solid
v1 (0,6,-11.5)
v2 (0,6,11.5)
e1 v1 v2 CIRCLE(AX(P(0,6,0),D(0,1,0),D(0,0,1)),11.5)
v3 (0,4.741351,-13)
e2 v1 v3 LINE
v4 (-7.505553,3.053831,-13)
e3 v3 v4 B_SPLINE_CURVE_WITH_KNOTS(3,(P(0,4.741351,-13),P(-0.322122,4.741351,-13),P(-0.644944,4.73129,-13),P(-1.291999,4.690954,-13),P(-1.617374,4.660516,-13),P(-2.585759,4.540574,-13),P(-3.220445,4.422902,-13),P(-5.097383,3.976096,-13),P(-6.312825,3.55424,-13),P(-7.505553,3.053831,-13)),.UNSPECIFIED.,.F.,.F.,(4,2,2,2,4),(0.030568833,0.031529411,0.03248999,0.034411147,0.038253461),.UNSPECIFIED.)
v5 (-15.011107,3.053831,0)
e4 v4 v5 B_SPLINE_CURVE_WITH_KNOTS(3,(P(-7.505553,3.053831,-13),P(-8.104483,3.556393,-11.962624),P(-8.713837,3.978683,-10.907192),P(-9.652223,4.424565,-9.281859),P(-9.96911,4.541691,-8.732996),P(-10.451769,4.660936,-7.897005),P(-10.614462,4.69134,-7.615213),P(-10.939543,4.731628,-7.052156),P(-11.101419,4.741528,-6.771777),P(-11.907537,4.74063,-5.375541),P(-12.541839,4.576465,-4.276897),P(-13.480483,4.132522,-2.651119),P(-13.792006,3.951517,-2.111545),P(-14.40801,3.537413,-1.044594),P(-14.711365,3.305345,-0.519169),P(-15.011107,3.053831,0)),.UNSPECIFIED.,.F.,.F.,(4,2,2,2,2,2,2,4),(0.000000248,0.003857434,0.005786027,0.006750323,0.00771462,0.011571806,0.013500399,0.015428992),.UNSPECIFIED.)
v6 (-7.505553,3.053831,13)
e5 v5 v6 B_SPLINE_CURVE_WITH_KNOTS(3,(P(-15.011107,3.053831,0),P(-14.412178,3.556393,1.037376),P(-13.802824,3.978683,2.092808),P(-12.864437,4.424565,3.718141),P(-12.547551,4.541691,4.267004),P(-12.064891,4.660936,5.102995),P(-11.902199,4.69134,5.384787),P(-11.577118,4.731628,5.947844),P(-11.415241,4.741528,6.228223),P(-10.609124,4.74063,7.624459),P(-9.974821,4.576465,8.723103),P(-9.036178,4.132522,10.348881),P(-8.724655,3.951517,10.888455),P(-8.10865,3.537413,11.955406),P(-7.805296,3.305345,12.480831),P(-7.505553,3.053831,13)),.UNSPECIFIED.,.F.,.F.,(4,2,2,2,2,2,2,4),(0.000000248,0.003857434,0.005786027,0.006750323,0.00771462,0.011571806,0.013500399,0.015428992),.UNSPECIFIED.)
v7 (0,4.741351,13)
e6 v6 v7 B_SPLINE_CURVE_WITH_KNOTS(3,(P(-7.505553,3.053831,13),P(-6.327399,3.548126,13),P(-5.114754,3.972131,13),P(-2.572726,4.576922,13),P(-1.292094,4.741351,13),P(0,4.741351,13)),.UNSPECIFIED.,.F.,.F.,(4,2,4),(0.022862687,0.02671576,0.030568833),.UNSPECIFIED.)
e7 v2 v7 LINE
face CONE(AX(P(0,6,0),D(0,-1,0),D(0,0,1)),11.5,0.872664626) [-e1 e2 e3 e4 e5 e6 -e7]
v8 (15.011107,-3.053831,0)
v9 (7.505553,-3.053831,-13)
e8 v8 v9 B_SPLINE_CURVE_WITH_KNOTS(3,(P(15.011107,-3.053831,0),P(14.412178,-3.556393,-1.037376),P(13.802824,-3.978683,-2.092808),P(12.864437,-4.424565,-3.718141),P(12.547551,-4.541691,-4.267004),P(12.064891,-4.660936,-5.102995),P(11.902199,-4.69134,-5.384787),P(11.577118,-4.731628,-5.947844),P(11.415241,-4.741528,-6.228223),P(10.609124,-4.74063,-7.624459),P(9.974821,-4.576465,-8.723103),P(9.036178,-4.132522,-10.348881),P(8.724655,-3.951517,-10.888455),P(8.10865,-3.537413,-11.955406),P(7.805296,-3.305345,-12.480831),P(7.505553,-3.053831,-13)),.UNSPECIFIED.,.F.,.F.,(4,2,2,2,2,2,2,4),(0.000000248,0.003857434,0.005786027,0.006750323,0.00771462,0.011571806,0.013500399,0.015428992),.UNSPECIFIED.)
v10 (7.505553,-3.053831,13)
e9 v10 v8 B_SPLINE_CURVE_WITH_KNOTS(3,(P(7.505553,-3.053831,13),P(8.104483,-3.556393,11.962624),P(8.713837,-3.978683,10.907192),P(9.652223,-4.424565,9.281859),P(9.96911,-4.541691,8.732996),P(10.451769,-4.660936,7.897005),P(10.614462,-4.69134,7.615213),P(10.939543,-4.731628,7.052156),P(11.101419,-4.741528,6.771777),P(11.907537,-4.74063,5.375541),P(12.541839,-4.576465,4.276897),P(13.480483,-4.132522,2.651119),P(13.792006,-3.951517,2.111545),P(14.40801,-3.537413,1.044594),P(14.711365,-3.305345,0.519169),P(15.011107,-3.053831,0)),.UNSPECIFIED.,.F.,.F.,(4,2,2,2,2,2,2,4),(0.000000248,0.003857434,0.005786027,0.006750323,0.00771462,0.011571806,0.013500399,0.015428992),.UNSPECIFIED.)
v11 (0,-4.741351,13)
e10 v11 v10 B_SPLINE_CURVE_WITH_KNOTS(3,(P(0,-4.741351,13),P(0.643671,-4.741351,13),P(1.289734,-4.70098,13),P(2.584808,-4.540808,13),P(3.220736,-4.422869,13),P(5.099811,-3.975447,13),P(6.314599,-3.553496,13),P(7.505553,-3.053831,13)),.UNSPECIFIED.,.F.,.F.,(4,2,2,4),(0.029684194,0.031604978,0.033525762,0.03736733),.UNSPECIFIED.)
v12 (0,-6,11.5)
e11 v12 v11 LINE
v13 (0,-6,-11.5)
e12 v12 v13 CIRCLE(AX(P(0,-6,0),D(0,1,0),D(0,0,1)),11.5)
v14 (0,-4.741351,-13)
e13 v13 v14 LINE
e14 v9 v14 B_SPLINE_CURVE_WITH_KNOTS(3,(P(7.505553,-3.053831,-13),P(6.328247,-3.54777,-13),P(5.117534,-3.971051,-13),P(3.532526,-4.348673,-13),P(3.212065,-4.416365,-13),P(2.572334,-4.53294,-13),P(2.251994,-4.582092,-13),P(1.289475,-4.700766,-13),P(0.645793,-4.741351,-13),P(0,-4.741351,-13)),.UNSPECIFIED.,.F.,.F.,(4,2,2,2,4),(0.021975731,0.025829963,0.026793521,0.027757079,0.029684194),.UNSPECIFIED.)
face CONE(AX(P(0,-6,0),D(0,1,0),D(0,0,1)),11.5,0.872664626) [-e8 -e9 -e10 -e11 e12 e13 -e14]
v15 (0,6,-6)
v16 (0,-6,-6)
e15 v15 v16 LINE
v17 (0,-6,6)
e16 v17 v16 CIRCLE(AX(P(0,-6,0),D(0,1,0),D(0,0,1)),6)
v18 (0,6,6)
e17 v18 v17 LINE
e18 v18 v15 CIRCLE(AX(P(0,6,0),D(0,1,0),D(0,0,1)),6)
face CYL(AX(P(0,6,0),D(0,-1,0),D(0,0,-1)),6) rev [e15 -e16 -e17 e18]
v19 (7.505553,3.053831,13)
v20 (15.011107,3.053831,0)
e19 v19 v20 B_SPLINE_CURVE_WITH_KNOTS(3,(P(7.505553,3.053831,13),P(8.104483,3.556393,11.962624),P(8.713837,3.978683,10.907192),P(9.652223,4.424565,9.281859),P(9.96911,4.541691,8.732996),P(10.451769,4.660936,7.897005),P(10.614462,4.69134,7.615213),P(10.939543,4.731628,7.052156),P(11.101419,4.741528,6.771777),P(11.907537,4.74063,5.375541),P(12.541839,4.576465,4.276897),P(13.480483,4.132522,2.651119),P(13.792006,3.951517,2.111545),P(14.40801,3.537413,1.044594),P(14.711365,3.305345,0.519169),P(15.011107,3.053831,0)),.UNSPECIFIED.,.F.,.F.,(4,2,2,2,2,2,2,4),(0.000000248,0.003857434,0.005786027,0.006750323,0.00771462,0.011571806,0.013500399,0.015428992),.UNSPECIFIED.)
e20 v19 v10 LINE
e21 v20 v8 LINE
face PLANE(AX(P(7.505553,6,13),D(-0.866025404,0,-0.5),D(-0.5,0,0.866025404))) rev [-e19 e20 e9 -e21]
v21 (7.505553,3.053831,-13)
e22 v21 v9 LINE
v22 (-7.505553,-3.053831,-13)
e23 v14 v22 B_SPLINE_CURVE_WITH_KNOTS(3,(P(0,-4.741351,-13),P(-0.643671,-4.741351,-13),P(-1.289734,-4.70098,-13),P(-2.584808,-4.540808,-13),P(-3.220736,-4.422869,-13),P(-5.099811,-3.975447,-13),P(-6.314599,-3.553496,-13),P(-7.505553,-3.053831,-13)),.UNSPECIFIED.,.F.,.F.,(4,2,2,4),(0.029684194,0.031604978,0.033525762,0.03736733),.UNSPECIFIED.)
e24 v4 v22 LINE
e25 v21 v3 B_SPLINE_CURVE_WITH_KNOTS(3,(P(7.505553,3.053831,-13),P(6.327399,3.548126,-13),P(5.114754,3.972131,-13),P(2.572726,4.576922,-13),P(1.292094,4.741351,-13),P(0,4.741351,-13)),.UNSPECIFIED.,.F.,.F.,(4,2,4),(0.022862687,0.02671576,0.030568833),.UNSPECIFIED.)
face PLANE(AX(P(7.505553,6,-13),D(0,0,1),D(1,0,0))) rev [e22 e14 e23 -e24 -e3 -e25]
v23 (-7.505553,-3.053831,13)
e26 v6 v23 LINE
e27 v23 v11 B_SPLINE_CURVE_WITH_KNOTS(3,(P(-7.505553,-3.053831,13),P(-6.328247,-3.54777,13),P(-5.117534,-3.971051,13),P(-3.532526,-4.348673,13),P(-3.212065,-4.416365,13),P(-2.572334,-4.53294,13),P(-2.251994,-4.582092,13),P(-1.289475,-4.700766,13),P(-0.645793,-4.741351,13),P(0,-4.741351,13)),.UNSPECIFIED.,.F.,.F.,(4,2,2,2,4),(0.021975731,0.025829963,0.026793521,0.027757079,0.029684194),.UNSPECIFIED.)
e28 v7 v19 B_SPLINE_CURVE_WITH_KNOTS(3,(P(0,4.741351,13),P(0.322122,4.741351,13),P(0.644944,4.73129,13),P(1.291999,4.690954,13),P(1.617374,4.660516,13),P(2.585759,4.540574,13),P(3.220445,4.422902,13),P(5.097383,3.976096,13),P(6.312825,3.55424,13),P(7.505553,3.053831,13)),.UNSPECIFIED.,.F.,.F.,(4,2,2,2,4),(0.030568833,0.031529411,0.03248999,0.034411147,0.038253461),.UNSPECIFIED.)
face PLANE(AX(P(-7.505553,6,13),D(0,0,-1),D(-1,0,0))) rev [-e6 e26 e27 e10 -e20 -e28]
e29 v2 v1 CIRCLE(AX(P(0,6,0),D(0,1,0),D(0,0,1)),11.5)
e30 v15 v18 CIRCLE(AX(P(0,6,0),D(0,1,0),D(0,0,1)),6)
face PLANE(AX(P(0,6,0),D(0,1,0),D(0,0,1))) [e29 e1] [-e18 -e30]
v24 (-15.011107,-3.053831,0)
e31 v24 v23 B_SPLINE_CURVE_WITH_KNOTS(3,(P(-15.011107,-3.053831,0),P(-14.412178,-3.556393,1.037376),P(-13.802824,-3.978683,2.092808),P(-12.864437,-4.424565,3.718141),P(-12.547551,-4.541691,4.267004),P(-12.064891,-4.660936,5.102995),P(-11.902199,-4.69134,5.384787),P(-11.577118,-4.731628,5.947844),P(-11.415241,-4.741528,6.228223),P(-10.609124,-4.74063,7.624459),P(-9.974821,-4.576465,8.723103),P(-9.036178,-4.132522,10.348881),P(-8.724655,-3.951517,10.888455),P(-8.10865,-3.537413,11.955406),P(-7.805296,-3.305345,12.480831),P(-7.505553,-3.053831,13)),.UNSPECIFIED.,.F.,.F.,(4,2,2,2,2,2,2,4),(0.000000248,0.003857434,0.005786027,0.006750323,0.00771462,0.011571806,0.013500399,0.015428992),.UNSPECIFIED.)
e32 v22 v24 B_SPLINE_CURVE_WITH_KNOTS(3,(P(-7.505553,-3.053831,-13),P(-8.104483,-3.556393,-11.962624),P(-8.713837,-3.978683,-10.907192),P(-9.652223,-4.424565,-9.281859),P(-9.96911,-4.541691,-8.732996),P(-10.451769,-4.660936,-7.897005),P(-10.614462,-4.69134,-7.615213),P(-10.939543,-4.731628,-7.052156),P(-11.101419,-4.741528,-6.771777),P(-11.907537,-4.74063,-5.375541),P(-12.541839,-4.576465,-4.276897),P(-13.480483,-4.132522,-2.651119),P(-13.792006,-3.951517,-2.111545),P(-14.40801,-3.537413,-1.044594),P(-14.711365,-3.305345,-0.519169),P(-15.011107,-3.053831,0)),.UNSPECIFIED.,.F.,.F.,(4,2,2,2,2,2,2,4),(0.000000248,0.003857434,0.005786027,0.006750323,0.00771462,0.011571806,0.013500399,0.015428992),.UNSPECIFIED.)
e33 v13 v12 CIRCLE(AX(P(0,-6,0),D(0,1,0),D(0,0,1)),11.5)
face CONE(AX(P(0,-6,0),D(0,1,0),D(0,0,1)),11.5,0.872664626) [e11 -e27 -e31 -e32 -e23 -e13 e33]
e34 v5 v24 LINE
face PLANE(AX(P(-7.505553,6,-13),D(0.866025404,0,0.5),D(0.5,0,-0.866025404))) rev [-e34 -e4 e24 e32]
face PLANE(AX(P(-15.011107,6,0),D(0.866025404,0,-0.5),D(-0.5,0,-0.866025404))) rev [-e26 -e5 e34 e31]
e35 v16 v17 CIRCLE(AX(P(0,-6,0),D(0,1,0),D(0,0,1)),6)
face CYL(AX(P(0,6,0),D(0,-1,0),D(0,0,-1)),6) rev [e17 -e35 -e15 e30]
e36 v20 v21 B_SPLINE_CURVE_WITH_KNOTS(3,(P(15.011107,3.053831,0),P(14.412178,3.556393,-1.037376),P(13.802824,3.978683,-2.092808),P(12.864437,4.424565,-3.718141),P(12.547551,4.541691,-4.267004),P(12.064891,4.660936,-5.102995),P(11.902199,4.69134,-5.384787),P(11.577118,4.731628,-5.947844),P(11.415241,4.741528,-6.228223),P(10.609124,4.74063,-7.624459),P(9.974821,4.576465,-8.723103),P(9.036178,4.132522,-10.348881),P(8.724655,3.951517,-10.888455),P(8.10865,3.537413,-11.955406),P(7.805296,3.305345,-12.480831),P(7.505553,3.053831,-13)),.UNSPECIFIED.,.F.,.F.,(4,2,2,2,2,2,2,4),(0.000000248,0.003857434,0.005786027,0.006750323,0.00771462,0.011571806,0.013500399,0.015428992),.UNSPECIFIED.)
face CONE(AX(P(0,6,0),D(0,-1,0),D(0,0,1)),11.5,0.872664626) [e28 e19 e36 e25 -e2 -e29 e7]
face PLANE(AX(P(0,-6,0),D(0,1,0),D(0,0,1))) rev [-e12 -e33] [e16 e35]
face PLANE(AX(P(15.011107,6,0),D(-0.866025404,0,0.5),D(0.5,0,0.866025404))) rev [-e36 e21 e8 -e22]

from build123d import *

# Parameters (mm, degrees)
HEX_NUT_PROFILE_R                     = 6
HEX_NUT_BODY_DEPTH                    = 6
CHAMFER_CIRCLE_23_OUTSIDE_W           = 98.006
CHAMFER_CIRCLE_23_OUTSIDE_H           = 93.984
CHAMFER_CIRCLE_23_OUTSIDE_R           = 11.5
CORNER_CHAMFER_50_DEPTH               = 24.202011407
CORNER_CHAMFER_50_DRAFT               = -50
CORNER_CHAMFER_MIRROR_COPY_1_SKETCH_W = 98.006
CORNER_CHAMFER_MIRROR_COPY_1_SKETCH_H = 93.984
CORNER_CHAMFER_MIRROR_COPY_1_SKETCH_R = 11.5
CORNER_CHAMFER_MIRROR_COPY_1_DEPTH    = 24.202011407
CORNER_CHAMFER_MIRROR_COPY_1_DRAFT    = -50


with BuildPart() as part:
    # Hex Nut Profile → Hex Nut Body (new, symmetric)
    with BuildSketch(Plane(origin=(0, 0, 0), x_dir=(1, 0, 0), z_dir=(0, 1, 0))):
        Polygon((15.011106999, 0), (7.505553499, 13), (-7.505553499, 13), (-15.011106999, 0), (-7.505553499, -13), (7.505553499, -13), align=None)
        with Locations(Location((0, 0, 0), (0, 0, 270))):
            Circle(HEX_NUT_PROFILE_R, mode=Mode.SUBTRACT)
    extrude(amount=HEX_NUT_BODY_DEPTH, both=True)


with BuildPart() as corner_chamfer_50_tool:
    # Chamfer Circle Ø23 outside → Corner Chamfer 50° (with draft: the straight prism first)
    with BuildSketch(Plane(origin=(0, 6, 0), x_dir=(1, 0, 0), z_dir=(0, 1, 0))):
        Rectangle(CHAMFER_CIRCLE_23_OUTSIDE_W, CHAMFER_CIRCLE_23_OUTSIDE_H)
        Circle(CHAMFER_CIRCLE_23_OUTSIDE_R, mode=Mode.SUBTRACT)
    extrude(amount=-CORNER_CHAMFER_50_DEPTH)
    # Corner Chamfer 50°: the draft: its side faces are tilted about the plane it starts from
    corner_chamfer_50_sides = [corner_chamfer_50_tool.faces().sort_by_distance(p)[0] for p in [
        (0, -6.101005704, 46.992),
        (49.003, -6.101005704, 0),
        (0, -6.101005704, -46.992),
        (-49.003, -6.101005704, 0),
        (-11.5, -6.101005704, 0),
    ]]
    draft(corner_chamfer_50_sides, Plane(origin=(0, 6, 0), x_dir=(1, 0, 0), z_dir=(0, 1, 0)), CORNER_CHAMFER_50_DRAFT)


with BuildPart() as part_1:
    add(part.part)

    # Corner Chamfer 50°: cut by corner_chamfer_50_tool
    add(corner_chamfer_50_tool.part, mode=Mode.SUBTRACT)


with BuildPart() as corner_chamfer_mirror_copy_1_tool:
    # Corner Chamfer Mirror copy 1 sketch → Corner Chamfer Mirror copy 1 (with draft: the straight prism first)
    with BuildSketch(Plane.XZ.offset(6)):
        Rectangle(CORNER_CHAMFER_MIRROR_COPY_1_SKETCH_W, CORNER_CHAMFER_MIRROR_COPY_1_SKETCH_H)
        Circle(CORNER_CHAMFER_MIRROR_COPY_1_SKETCH_R, mode=Mode.SUBTRACT)
    extrude(amount=-CORNER_CHAMFER_MIRROR_COPY_1_DEPTH)
    # Corner Chamfer Mirror copy 1: the draft: its side faces are tilted about the plane it starts from
    corner_chamfer_mirror_copy_1_sides = [corner_chamfer_mirror_copy_1_tool.faces().sort_by_distance(p)[0] for p in [
        (0, 6.101005704, 46.992),
        (49.003, 6.101005704, 0),
        (0, 6.101005704, -46.992),
        (-49.003, 6.101005704, 0),
        (-11.5, 6.101005704, 0),
    ]]
    draft(corner_chamfer_mirror_copy_1_sides, Plane.XZ.offset(6), CORNER_CHAMFER_MIRROR_COPY_1_DRAFT)


with BuildPart() as part_2:
    add(part_1.part)

    # Corner Chamfer Mirror copy 1: cut by corner_chamfer_mirror_copy_1_tool
    add(corner_chamfer_mirror_copy_1_tool.part, mode=Mode.SUBTRACT)


solid = part_2.part
